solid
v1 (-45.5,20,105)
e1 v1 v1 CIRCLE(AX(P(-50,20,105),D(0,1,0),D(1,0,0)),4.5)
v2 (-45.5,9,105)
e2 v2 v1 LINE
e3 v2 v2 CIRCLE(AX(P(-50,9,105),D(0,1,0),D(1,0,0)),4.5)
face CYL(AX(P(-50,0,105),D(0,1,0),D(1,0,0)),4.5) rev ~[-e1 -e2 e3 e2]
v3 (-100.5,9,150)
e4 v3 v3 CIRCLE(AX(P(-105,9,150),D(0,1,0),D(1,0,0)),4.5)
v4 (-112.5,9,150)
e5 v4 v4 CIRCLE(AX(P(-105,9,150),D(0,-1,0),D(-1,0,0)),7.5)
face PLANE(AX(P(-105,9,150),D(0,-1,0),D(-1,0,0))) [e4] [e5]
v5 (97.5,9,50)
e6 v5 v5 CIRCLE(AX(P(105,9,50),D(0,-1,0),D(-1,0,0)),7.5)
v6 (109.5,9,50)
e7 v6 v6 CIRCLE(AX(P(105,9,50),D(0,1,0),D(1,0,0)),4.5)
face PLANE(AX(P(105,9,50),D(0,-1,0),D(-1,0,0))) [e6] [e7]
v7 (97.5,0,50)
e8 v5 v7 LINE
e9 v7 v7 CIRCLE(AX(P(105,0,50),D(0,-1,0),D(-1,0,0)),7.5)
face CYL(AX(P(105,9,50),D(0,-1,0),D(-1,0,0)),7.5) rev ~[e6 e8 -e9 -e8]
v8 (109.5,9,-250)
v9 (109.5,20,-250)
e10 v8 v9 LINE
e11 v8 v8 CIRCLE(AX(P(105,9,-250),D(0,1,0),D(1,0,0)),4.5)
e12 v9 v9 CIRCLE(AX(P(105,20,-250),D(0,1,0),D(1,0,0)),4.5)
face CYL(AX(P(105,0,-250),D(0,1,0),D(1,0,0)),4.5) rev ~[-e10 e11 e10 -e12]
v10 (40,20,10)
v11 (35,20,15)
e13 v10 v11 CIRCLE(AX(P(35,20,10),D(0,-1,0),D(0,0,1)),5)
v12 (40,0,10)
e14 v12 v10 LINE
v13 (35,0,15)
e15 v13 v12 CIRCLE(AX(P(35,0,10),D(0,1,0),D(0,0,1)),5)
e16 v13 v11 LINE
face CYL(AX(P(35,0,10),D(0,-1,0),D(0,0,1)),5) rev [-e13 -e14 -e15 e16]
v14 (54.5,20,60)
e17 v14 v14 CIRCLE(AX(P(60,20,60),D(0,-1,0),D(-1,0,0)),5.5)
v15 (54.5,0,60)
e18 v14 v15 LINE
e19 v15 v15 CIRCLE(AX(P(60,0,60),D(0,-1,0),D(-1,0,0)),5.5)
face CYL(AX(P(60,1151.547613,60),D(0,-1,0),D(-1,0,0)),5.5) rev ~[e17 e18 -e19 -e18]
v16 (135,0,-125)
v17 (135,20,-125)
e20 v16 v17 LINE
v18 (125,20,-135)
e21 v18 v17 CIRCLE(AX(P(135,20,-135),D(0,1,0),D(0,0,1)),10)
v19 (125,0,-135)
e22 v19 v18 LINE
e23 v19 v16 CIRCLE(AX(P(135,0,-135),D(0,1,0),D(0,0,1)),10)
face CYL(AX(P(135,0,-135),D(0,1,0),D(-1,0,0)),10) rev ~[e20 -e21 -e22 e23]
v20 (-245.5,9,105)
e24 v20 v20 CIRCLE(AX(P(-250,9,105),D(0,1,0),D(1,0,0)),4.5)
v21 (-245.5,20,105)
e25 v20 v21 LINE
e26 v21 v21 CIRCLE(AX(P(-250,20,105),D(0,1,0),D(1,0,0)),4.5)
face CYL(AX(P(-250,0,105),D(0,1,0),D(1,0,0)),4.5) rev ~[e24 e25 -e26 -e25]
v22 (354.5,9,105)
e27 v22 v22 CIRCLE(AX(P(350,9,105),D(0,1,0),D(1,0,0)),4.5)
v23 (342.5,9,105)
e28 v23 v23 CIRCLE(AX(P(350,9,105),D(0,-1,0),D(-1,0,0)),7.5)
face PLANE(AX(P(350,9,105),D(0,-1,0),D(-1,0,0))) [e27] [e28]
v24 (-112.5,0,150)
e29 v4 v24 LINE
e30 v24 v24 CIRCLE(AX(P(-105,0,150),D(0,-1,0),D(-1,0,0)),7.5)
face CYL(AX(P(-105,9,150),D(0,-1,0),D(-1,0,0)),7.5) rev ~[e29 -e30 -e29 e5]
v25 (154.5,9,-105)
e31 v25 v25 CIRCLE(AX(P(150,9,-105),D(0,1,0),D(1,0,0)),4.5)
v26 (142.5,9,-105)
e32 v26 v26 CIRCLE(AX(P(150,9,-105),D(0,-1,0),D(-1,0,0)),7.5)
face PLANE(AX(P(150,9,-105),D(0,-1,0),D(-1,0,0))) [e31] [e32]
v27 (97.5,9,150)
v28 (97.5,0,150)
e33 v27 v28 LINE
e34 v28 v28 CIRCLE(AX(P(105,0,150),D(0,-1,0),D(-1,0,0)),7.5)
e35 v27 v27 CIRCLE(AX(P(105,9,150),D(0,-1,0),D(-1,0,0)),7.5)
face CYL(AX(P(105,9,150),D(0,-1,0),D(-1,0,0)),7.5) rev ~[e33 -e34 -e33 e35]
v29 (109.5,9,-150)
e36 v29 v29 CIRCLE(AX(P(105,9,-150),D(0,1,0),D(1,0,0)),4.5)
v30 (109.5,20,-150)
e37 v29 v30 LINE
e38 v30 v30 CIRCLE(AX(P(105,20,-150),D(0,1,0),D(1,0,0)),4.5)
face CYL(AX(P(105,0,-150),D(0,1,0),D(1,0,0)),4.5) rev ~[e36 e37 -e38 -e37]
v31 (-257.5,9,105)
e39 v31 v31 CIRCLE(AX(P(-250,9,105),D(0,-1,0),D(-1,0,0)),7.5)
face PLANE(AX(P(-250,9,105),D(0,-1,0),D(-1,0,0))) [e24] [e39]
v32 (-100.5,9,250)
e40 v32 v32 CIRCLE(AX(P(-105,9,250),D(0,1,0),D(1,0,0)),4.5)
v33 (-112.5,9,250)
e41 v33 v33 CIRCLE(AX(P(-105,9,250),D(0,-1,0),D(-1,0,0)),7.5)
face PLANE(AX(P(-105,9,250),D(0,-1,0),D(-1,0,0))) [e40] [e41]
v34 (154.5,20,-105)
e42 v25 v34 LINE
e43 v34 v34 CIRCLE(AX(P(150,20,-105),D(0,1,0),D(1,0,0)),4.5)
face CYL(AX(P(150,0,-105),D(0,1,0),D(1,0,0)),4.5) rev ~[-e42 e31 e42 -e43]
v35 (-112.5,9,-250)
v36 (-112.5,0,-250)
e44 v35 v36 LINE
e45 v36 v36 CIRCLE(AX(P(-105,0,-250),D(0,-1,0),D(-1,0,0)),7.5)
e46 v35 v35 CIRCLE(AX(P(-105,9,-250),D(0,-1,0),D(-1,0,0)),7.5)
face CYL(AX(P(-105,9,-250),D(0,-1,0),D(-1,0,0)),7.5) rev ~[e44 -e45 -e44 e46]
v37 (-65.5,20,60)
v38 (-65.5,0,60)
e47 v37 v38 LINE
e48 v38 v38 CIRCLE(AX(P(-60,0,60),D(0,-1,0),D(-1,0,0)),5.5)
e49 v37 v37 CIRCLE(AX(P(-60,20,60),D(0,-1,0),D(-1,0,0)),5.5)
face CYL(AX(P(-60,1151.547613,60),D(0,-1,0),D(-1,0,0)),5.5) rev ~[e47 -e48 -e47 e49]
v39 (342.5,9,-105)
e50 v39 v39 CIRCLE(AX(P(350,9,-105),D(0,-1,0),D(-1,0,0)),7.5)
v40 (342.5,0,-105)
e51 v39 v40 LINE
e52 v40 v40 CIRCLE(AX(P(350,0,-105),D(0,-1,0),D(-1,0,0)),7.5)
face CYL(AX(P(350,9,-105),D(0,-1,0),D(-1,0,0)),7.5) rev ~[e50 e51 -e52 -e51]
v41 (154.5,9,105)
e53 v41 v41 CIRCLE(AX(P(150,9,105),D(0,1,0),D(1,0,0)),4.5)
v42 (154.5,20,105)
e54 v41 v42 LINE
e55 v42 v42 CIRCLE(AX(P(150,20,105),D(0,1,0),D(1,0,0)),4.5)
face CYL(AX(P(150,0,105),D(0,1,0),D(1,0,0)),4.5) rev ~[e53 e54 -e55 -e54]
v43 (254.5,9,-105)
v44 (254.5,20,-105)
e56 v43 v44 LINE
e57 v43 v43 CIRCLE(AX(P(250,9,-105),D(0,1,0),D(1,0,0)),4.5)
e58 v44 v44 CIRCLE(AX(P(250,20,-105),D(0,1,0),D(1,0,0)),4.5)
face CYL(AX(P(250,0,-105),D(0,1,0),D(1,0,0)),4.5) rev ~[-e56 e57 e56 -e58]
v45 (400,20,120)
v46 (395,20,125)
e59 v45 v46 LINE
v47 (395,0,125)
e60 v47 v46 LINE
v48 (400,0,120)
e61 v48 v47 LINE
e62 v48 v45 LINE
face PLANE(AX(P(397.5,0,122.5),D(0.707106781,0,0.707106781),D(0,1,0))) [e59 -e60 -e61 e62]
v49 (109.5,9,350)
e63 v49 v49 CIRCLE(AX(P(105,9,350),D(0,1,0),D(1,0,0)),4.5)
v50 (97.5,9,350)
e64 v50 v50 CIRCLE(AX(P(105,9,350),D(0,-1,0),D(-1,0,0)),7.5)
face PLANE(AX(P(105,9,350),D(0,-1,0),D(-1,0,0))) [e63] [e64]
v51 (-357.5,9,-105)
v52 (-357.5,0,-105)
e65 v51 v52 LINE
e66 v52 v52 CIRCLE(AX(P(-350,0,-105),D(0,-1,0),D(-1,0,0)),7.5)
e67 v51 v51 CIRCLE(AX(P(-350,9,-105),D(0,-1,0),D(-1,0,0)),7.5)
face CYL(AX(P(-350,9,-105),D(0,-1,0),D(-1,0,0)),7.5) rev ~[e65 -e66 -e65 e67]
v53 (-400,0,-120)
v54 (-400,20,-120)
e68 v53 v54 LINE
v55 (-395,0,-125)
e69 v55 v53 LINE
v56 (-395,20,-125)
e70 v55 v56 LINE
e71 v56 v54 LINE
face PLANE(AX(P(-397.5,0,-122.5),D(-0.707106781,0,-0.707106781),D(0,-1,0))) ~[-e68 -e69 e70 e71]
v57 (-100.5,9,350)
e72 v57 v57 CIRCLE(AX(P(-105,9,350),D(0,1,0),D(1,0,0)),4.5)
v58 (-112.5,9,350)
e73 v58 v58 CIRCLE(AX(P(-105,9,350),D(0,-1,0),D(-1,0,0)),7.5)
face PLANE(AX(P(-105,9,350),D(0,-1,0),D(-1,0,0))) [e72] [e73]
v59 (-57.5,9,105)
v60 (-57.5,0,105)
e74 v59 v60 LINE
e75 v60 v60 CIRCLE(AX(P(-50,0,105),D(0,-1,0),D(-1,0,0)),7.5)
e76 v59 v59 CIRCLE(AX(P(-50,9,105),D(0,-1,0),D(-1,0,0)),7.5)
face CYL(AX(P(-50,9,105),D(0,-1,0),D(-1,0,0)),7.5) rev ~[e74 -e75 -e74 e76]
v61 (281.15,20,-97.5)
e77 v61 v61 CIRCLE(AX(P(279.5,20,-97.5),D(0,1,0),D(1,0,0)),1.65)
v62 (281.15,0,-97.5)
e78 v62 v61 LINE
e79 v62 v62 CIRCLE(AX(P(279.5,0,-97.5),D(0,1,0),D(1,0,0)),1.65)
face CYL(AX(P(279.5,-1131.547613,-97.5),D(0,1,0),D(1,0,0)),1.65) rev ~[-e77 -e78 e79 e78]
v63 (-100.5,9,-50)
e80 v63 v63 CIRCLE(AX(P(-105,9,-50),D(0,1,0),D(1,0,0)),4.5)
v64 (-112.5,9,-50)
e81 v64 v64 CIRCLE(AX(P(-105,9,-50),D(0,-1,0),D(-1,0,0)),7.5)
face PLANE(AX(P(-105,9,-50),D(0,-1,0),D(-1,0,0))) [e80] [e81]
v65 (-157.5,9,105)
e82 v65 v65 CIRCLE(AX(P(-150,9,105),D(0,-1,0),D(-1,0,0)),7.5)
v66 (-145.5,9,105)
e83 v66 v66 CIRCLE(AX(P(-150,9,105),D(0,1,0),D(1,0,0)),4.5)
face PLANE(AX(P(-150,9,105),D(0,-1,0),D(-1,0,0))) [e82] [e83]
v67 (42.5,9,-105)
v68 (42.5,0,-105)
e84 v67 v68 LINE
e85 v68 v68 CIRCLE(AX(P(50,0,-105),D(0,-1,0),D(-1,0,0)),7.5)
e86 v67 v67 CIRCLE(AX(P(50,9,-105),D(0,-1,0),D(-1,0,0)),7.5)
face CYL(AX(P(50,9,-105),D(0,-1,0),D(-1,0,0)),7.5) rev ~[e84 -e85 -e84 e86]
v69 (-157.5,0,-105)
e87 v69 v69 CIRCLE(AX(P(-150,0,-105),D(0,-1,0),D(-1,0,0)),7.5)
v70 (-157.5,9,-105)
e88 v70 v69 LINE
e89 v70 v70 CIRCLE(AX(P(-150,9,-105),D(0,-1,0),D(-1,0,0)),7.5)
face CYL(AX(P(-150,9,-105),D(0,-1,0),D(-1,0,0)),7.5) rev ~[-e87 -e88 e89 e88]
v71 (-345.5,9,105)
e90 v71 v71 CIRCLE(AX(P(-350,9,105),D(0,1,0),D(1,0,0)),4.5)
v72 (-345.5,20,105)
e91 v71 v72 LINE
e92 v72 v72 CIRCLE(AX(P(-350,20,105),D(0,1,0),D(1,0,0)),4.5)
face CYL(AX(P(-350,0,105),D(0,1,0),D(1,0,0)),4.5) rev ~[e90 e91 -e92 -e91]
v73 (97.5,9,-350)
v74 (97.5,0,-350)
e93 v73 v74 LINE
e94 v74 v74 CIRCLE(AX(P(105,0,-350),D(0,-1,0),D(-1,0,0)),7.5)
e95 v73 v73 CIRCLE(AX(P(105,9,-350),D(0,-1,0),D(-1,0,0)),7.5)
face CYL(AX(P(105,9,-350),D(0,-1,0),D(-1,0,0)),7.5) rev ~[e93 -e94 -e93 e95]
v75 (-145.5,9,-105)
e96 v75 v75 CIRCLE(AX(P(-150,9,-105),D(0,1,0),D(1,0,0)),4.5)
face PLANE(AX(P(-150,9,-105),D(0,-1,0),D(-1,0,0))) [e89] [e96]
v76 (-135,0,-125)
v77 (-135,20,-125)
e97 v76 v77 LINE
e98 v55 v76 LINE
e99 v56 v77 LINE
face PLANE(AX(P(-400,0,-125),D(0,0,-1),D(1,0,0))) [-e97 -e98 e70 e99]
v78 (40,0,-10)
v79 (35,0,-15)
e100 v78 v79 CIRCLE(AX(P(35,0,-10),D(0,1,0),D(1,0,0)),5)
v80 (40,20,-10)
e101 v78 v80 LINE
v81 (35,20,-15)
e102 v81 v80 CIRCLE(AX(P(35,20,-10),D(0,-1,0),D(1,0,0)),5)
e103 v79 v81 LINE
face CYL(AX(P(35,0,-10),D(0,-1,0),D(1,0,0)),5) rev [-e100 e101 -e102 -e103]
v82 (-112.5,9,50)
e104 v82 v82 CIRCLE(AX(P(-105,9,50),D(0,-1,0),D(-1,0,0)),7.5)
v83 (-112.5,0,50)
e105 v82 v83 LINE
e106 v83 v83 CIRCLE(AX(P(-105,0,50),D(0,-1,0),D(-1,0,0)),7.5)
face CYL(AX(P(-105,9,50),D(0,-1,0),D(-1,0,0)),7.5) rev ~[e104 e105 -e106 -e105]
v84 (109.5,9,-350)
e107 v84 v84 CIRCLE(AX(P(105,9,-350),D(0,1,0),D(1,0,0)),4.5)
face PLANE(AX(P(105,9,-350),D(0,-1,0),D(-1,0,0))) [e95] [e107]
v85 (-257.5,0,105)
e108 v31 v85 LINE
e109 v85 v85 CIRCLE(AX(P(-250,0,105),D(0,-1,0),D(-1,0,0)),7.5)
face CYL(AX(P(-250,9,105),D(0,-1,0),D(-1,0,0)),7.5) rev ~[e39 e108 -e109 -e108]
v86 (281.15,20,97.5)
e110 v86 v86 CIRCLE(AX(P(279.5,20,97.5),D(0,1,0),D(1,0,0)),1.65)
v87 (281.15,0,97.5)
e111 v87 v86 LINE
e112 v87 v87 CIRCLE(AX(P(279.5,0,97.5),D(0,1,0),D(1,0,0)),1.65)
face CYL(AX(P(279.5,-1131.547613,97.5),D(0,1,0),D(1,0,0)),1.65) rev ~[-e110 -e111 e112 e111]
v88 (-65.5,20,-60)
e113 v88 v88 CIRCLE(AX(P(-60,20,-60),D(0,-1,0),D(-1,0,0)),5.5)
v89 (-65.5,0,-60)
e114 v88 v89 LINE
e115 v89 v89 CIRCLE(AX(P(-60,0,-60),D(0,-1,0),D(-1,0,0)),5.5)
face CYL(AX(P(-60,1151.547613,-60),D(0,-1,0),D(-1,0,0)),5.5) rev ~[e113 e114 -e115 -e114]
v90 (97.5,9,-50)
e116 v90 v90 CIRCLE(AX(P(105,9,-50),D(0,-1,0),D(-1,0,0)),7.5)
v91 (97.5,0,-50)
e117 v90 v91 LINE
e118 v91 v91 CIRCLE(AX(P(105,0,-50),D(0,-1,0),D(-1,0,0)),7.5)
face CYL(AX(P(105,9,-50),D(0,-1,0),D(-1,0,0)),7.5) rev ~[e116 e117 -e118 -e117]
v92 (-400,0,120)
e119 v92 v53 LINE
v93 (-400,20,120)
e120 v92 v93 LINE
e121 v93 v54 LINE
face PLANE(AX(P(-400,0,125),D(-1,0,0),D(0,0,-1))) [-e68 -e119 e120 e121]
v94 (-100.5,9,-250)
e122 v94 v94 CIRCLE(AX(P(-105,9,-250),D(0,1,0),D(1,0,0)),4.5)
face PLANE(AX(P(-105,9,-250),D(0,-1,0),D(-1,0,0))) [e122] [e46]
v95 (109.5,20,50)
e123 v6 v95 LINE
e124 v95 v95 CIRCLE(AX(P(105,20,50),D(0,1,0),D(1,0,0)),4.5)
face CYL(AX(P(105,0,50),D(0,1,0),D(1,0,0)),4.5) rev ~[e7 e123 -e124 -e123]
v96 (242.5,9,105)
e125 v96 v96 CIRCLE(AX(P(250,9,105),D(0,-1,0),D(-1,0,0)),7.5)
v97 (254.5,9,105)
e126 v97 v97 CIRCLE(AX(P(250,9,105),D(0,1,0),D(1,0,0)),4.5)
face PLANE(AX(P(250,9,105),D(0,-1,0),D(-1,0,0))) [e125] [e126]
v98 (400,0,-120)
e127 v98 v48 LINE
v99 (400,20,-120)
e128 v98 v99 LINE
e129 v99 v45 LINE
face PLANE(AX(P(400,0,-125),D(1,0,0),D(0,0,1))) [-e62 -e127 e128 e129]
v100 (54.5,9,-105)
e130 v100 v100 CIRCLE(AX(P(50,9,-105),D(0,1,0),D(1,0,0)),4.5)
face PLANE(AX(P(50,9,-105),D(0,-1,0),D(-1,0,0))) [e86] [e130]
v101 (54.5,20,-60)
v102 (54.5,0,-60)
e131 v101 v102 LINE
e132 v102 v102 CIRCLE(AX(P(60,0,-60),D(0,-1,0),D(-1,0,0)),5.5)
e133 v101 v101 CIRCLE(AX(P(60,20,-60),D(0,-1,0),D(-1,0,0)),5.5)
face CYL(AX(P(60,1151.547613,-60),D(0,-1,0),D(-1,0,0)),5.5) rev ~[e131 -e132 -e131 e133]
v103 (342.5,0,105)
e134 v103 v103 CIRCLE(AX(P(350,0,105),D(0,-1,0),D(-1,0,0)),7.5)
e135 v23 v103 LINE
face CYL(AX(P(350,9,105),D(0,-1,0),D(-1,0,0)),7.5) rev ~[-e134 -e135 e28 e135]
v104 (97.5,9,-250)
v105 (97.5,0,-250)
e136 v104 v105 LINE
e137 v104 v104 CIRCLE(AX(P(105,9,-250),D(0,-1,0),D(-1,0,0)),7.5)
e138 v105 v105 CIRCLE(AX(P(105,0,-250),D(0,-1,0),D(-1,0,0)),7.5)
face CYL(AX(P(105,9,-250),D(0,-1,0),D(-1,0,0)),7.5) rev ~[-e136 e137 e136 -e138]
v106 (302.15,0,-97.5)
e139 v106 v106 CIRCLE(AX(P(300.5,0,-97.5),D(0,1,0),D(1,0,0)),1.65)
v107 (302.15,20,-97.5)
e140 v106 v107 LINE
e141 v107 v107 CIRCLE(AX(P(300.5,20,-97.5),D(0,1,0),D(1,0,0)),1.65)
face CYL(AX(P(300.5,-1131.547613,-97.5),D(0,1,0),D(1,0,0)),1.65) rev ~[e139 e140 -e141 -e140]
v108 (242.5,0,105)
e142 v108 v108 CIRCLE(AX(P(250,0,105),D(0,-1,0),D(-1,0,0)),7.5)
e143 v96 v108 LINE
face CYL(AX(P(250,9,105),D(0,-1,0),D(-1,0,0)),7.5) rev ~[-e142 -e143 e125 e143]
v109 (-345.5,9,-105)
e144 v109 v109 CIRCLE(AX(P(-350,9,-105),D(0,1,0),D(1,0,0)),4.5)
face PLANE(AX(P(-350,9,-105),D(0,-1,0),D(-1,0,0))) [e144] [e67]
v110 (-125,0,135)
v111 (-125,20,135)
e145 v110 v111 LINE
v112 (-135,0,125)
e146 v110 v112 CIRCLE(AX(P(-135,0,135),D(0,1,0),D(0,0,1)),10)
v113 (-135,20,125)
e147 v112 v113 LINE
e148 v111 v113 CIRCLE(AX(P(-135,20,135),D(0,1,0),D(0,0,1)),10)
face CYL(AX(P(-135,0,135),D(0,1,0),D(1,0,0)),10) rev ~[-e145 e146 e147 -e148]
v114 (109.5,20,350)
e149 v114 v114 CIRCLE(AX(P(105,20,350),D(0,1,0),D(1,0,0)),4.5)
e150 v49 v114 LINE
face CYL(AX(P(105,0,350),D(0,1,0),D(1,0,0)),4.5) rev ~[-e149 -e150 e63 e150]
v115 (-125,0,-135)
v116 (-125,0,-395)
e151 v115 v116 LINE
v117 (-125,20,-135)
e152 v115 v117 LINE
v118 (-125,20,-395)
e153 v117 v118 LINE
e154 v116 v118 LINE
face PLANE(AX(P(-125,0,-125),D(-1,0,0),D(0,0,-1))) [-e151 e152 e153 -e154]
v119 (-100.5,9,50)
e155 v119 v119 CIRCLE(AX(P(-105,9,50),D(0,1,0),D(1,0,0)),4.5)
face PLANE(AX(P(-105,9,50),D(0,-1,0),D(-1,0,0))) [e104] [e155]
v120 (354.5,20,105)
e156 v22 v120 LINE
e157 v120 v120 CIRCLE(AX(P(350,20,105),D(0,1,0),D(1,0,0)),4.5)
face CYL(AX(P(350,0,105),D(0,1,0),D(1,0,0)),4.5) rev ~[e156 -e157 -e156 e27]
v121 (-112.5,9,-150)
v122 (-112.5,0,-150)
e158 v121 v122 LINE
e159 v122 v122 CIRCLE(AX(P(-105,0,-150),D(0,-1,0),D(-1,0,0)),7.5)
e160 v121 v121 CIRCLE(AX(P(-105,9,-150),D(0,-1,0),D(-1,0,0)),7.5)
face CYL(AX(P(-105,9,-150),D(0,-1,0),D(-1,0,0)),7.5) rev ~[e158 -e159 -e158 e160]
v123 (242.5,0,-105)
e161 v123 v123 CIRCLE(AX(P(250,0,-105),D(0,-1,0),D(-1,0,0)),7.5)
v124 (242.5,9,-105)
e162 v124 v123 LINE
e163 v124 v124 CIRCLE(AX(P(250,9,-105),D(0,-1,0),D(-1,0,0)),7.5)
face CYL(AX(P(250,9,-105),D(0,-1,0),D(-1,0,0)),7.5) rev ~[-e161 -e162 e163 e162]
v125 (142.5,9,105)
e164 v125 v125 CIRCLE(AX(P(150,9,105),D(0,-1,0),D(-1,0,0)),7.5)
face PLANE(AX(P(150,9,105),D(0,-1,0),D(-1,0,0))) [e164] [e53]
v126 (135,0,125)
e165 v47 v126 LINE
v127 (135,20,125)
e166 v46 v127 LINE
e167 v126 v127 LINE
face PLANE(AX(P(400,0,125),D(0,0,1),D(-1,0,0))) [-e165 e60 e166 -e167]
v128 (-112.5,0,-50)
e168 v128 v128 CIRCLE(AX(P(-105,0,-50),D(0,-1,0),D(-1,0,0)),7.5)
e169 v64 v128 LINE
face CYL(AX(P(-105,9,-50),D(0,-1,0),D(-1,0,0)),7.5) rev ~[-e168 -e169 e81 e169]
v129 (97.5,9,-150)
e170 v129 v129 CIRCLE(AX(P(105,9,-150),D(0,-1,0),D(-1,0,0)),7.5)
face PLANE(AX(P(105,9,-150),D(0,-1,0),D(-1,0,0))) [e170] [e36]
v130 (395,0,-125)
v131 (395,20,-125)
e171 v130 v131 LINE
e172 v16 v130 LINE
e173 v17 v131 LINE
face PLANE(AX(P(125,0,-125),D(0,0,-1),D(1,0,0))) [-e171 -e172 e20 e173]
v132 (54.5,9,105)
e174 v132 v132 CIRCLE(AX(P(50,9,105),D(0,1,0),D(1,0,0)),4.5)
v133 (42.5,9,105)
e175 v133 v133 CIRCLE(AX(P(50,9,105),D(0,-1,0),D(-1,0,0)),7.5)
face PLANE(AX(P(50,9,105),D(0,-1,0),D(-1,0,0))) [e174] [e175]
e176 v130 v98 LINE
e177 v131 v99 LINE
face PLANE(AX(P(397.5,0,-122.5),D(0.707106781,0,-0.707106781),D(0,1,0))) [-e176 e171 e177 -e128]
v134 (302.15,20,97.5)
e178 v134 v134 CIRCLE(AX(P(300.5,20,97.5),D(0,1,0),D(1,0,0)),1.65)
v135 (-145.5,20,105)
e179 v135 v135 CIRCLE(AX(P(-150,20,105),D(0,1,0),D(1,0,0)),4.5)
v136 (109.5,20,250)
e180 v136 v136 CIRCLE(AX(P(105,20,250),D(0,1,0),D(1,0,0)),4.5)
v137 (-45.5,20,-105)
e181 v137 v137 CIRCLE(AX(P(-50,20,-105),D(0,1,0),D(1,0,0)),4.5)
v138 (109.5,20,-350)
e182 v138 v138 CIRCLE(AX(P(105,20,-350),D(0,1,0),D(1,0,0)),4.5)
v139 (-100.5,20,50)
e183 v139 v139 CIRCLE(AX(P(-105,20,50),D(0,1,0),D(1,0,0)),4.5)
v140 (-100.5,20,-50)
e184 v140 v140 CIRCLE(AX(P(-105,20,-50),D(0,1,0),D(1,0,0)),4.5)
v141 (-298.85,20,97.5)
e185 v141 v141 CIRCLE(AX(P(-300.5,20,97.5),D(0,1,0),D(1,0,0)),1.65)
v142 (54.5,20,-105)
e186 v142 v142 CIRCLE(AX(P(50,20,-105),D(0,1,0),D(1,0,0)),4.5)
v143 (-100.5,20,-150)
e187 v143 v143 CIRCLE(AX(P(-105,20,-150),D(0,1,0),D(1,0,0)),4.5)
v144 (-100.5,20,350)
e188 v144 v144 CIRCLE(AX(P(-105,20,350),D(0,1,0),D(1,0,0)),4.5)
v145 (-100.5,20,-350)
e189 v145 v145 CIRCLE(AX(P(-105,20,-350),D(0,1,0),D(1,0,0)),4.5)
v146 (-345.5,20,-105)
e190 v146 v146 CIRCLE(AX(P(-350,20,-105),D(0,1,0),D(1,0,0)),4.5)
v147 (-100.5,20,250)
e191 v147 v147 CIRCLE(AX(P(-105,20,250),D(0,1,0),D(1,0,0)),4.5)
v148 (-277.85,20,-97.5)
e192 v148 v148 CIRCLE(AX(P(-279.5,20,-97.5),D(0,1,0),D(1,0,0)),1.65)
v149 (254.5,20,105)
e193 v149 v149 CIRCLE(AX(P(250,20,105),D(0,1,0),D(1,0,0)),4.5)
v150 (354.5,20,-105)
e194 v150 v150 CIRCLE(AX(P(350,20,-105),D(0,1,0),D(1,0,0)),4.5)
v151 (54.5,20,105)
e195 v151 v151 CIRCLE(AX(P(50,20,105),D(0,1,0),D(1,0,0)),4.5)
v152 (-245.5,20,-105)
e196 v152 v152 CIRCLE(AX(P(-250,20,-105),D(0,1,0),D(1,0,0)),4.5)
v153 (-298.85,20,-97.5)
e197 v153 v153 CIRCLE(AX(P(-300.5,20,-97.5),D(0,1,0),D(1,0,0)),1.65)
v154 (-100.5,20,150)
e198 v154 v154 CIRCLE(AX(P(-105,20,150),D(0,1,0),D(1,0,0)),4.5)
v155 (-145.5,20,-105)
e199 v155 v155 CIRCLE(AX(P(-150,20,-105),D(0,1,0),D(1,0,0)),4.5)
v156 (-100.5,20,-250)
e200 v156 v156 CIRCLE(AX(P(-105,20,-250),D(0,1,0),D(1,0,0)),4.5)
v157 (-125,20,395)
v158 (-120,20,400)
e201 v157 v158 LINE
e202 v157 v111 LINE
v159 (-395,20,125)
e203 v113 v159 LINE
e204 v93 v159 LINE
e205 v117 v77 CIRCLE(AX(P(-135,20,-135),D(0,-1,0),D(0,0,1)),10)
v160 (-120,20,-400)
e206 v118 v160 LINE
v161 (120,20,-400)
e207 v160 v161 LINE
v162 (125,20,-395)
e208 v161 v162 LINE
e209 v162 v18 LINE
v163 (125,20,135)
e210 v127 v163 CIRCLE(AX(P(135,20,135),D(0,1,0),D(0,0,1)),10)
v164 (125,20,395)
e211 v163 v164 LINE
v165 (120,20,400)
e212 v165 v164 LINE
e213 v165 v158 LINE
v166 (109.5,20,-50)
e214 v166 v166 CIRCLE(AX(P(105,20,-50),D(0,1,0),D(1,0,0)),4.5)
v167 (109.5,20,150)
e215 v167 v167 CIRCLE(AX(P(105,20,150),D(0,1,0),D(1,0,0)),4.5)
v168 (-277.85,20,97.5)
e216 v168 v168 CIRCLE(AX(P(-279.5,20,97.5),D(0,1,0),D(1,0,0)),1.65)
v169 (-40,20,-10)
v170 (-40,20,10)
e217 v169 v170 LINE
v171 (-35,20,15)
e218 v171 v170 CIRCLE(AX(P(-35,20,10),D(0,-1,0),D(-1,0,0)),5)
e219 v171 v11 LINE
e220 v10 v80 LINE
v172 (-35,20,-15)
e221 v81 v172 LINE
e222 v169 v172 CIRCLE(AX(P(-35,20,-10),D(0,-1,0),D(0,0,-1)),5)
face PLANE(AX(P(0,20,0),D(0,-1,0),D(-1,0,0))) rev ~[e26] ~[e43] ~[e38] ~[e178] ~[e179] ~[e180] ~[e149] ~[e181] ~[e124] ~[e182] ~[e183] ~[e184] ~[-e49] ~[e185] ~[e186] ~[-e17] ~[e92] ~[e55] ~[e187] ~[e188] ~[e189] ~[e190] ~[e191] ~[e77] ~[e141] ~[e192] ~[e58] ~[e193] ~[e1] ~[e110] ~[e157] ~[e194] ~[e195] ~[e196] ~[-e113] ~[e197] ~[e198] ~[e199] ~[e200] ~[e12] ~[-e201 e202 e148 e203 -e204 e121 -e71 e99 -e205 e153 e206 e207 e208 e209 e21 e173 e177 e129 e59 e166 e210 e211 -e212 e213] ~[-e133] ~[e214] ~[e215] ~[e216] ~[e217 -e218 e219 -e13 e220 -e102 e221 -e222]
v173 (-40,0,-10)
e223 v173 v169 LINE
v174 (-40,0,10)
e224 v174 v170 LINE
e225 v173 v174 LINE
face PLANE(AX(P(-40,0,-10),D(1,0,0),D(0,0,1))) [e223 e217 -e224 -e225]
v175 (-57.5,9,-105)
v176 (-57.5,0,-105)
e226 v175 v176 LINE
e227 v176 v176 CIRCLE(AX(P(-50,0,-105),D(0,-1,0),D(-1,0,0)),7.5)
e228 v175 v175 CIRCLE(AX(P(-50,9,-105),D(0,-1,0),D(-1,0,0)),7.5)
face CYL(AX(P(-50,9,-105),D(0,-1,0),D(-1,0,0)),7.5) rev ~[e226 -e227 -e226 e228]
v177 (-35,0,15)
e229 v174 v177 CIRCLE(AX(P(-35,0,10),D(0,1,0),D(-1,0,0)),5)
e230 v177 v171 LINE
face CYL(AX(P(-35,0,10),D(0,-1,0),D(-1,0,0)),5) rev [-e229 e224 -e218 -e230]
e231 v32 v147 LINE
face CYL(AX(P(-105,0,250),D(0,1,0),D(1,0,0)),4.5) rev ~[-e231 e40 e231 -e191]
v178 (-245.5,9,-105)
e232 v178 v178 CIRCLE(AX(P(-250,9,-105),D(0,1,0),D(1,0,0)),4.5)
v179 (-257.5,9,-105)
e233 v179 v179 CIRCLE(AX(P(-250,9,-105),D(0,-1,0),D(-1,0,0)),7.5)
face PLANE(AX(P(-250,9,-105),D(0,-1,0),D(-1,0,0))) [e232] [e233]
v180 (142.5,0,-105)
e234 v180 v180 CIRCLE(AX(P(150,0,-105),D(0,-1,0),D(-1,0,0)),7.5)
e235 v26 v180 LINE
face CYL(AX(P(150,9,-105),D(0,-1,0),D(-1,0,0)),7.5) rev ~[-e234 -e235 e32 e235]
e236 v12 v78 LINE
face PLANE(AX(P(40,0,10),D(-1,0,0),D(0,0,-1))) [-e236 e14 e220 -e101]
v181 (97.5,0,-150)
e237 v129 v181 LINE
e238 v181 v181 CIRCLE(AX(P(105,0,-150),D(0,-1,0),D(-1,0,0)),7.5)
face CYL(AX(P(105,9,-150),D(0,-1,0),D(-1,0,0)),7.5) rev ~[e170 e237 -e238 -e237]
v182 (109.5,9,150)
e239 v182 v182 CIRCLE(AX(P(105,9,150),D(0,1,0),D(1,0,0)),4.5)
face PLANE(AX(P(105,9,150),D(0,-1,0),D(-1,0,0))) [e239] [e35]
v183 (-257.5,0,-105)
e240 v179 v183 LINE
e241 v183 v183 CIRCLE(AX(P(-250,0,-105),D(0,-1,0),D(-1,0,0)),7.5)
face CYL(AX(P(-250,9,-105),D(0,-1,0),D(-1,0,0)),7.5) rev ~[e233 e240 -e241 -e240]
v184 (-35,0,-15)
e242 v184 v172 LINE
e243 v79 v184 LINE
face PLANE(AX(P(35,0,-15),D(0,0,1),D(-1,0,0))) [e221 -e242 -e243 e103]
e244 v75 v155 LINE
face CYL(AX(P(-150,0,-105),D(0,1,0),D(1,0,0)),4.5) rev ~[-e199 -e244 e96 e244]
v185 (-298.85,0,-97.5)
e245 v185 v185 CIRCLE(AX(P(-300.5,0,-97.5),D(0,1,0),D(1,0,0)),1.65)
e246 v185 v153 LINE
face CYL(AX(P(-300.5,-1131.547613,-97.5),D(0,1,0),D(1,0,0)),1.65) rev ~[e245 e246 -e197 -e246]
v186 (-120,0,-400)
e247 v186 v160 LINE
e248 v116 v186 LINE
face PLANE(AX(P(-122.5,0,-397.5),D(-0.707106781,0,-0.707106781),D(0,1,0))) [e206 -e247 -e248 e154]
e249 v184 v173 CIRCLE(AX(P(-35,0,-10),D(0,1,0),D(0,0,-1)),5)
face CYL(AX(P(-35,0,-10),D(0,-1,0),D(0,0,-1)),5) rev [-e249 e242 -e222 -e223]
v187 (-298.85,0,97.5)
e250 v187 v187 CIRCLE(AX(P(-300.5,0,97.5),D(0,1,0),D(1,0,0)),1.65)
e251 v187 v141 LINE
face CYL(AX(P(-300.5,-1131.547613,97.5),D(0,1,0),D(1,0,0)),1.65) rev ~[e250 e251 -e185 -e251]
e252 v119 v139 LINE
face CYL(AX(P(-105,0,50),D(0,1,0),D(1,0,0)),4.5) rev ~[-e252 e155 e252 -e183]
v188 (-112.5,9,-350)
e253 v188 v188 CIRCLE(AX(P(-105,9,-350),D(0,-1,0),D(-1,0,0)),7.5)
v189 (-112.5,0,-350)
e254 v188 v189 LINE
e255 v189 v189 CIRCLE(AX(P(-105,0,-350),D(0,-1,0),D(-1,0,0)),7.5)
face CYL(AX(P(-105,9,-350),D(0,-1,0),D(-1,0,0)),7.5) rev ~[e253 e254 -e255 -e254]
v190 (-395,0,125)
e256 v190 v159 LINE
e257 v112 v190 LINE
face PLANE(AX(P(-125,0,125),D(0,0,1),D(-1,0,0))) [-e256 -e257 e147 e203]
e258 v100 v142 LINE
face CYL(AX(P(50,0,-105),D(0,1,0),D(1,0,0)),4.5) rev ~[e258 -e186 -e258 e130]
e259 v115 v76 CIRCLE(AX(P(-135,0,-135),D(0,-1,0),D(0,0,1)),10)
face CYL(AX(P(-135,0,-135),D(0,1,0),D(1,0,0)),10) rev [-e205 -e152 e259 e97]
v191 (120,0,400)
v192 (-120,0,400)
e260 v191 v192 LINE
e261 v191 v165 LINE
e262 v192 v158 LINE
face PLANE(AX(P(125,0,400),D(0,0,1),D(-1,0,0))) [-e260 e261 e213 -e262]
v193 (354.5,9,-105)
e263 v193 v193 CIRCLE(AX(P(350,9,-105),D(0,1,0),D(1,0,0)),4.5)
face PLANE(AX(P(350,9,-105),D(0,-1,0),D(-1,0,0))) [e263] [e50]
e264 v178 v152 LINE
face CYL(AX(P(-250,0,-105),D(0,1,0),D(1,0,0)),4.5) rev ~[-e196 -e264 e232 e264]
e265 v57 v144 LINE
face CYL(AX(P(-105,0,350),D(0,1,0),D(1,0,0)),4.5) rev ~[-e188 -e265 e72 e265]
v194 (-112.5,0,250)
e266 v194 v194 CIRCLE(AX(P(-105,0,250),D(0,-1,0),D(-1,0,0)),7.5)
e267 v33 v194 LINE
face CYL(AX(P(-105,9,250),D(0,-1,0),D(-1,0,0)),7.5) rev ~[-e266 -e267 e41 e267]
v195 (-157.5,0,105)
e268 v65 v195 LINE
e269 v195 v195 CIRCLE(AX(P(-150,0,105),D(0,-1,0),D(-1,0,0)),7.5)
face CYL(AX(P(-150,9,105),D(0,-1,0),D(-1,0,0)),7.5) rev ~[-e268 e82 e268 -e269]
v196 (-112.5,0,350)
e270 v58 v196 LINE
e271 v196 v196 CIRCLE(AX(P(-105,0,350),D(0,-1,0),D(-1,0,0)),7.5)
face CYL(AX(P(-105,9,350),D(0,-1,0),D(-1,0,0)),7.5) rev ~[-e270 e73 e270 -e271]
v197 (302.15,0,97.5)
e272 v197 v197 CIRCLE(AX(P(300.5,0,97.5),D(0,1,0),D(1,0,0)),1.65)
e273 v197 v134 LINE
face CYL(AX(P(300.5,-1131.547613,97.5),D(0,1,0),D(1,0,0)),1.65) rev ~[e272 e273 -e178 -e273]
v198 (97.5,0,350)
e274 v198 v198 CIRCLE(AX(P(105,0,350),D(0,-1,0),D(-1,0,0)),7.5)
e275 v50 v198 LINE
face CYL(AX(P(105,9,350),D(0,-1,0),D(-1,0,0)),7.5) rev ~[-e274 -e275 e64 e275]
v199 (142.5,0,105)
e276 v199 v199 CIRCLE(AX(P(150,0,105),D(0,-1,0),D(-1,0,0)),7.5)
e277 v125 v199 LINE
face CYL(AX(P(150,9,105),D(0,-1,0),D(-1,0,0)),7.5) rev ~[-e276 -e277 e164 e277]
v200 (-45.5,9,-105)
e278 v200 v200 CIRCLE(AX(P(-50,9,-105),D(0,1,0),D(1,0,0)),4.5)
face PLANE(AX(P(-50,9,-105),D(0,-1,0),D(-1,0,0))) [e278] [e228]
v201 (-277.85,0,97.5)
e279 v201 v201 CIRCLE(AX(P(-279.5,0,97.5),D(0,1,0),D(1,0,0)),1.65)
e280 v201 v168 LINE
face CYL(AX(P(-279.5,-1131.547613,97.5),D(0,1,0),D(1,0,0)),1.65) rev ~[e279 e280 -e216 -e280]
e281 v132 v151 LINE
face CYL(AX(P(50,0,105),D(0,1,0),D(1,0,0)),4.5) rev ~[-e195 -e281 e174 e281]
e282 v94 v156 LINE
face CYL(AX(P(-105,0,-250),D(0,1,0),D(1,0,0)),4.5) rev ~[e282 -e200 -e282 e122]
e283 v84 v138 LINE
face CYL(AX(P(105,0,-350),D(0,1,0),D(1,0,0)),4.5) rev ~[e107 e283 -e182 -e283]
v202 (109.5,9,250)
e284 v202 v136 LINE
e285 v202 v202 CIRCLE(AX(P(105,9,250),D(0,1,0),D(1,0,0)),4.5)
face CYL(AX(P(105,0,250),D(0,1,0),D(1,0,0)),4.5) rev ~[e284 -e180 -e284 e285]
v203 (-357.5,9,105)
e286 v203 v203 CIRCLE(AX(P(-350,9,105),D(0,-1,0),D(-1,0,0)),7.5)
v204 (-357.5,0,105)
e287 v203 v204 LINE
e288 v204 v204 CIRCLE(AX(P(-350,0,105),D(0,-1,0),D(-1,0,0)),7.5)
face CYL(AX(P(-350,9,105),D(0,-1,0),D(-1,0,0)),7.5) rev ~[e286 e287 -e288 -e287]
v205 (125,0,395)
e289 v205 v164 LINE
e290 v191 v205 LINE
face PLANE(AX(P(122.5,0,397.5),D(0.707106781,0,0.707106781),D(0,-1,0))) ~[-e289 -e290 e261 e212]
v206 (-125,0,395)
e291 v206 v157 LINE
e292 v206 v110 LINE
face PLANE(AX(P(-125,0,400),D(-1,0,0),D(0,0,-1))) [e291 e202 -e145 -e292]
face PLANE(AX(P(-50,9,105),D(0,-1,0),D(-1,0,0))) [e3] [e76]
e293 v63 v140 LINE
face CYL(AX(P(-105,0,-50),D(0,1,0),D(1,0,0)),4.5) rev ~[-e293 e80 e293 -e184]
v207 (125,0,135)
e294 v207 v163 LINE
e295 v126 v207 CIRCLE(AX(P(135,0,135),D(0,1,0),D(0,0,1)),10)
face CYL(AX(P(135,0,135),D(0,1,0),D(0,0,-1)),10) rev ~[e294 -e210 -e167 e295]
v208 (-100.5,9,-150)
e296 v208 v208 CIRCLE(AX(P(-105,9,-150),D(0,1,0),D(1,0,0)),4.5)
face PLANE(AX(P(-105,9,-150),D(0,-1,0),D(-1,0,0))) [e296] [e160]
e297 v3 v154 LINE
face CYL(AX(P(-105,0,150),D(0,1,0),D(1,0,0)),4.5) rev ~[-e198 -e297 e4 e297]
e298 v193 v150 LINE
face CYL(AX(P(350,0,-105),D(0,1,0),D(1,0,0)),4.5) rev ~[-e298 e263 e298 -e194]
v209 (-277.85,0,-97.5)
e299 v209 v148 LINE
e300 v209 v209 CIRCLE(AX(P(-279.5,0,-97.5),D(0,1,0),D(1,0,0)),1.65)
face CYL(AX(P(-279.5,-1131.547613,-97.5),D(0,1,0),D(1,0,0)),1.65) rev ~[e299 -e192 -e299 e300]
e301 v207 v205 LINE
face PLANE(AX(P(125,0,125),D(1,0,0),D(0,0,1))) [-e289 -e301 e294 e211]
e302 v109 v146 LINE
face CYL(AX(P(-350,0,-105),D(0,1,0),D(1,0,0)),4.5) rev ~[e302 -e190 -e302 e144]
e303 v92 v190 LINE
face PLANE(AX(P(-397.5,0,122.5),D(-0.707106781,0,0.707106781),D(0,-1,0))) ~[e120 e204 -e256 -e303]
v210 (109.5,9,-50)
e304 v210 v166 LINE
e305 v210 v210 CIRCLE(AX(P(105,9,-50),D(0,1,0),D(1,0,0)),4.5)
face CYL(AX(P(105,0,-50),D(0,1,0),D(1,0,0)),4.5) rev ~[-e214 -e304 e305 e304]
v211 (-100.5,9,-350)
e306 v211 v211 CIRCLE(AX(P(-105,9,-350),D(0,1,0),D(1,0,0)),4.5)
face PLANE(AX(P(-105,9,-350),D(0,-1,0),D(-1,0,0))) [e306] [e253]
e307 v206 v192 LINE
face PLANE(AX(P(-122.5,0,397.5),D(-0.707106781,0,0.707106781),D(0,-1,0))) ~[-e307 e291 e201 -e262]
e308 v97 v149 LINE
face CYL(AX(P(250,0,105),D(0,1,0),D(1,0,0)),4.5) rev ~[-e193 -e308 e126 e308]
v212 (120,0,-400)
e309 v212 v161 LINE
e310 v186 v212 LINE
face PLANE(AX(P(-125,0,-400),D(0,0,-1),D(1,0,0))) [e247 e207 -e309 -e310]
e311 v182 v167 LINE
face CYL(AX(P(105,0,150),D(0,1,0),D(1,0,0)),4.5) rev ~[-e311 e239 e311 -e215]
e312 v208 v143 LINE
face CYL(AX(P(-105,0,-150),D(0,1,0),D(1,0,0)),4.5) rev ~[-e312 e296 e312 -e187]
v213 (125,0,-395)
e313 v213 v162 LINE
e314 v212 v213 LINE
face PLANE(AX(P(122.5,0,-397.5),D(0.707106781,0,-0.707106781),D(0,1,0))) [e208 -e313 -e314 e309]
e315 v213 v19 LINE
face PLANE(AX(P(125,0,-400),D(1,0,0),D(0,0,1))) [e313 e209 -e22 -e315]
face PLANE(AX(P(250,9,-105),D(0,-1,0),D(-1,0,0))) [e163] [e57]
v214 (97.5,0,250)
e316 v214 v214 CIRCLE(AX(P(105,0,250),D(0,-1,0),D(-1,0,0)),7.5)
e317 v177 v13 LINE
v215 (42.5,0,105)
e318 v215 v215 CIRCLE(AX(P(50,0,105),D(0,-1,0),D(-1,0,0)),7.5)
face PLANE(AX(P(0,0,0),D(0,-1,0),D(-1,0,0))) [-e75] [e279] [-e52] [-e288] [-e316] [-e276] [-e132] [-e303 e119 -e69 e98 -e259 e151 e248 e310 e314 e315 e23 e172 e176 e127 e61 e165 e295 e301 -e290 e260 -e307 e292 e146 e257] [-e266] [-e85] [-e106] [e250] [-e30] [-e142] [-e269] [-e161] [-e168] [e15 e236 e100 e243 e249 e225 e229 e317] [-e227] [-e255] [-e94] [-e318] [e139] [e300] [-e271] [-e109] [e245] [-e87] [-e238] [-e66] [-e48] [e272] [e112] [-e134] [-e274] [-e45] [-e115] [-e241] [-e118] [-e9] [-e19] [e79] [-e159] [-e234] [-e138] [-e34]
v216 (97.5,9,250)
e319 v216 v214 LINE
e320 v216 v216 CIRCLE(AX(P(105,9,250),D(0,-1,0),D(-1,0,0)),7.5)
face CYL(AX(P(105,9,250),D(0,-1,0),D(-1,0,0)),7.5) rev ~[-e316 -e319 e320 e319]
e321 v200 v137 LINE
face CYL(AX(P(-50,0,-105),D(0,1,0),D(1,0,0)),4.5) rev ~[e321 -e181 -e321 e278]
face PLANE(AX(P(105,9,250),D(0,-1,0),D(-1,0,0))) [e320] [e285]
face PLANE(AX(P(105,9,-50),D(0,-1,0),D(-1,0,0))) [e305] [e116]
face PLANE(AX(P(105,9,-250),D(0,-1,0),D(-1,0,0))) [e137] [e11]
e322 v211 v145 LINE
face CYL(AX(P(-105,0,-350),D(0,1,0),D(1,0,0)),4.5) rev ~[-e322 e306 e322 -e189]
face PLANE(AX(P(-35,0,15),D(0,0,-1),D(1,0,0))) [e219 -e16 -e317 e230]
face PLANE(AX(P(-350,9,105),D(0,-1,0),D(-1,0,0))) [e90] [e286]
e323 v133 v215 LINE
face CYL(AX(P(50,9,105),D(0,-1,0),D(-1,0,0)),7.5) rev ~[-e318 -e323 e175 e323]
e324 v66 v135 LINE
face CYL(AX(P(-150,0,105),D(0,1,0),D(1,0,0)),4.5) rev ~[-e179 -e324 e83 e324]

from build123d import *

# Parameters (mm, degrees)
EXTRUDE_1_DEPTH              = 20
FILLET_1_R                   = 10
CHAMFER_1_SIZE               = 5
CUT_EXTRUDE_1_DEPTH          = 567.038867923
HOLE_WIZARD_M10_1_D          = 11
HOLE_WIZARD_M8_1_D           = 9
HOLE_WIZARD_M8_1_CBORE_D     = 15
HOLE_WIZARD_M8_1_CBORE_DEPTH = 9
HOLE_WIZARD_M4_1_D           = 3.3


with BuildPart() as part:
    # 草图1 → 凸台-拉伸1 (new body)
    with BuildSketch(Plane(origin=(0, 0, 0), x_dir=(1, 0, 0), z_dir=(0, 1, 0))):
        Polygon((-125, 125), (-125, 400), (125, 400), (125, 125), (400, 125), (400, -125), (125, -125), (125, -400), (-125, -400), (-125, -125), (-400, -125), (-400, 125), align=None)
    extrude(amount=EXTRUDE_1_DEPTH)

    # 圆角1
    fillet_1_edges = [part.edges().sort_by_distance(p)[0] for p in [
        (-125, 10, 125),
        (-125, 10, -125),
        (125, 10, -125),
        (125, 10, 125),
    ]]
    fillet(fillet_1_edges, radius=FILLET_1_R)

    # 倒角1
    chamfer_1_edges = [part.edges().sort_by_distance(p)[0] for p in [
        (-400, 10, 125),
        (-400, 10, -125),
        (-125, 10, -400),
        (125, 10, -400),
        (400, 10, -125),
        (400, 10, 125),
        (125, 10, 400),
        (-125, 10, 400),
    ]]
    chamfer(chamfer_1_edges, length=CHAMFER_1_SIZE)

    # 草图2 → 切除-拉伸1 (cut, through all)
    with BuildSketch(Plane.XZ):
        with BuildLine():
            Line((-35, 15), (35, 15))
            ThreePointArc((35, 15), (38.535533906, 13.535533906), (40, 10))
            Line((40, 10), (40, -10))
            ThreePointArc((40, -10), (38.535533906, -13.535533906), (35, -15))
            Line((35, -15), (-35, -15))
            ThreePointArc((-35, -15), (-38.535533906, -13.535533906), (-40, -10))
            Line((-40, -10), (-40, 10))
            ThreePointArc((-40, 10), (-38.535533906, 13.535533906), (-35, 15))
        make_face()
    extrude(amount=-CUT_EXTRUDE_1_DEPTH, mode=Mode.SUBTRACT)

    # M10 间隙孔1 (through all)
    with Locations(Plane(origin=(0, 20, 0), x_dir=(1, 0, 0), z_dir=(0, 1, 0))):
        with Locations((-60, 60), (60, 60), (60, -60), (-60, -60)):
            Hole(HOLE_WIZARD_M10_1_D / 2)

    # M8 六角圆柱头螺钉的柱形沉头孔1 (through all)
    with Locations(Plane(origin=(0, 0, 0), x_dir=(-1, 0, 0), z_dir=(0, -1, 0))):
        with Locations((-105, 350), (-105, 250), (-105, 150), (-105, 50), (-350, 105), (-250, 105), (-150, 105), (-50, 105), (50, 105), (150, 105), (250, 105), (350, 105), (105, 50), (105, 150), (105, 250), (105, 350), (0, 0), (105, -350), (105, -250), (105, -150), (105, -50), (350, -105), (250, -105), (150, -105), (50, -105), (-50, -105), (-150, -105), (-250, -105), (-350, -105), (-105, -50), (-105, -150), (-105, -250), (-105, -350)):
            CounterBoreHole(HOLE_WIZARD_M8_1_D / 2, HOLE_WIZARD_M8_1_CBORE_D / 2, HOLE_WIZARD_M8_1_CBORE_DEPTH)

    # M4 螺纹孔1 (through all)
    with Locations(Plane(origin=(0, 0, 0), x_dir=(-1, 0, 0), z_dir=(0, -1, 0))):
        with Locations((-300.5, 97.5), (-279.5, 97.5), (-279.5, -97.5), (-300.5, -97.5), (300.5, -97.5), (279.5, -97.5), (279.5, 97.5), (300.5, 97.5)):
            Hole(HOLE_WIZARD_M4_1_D / 2)


solid = part.part
